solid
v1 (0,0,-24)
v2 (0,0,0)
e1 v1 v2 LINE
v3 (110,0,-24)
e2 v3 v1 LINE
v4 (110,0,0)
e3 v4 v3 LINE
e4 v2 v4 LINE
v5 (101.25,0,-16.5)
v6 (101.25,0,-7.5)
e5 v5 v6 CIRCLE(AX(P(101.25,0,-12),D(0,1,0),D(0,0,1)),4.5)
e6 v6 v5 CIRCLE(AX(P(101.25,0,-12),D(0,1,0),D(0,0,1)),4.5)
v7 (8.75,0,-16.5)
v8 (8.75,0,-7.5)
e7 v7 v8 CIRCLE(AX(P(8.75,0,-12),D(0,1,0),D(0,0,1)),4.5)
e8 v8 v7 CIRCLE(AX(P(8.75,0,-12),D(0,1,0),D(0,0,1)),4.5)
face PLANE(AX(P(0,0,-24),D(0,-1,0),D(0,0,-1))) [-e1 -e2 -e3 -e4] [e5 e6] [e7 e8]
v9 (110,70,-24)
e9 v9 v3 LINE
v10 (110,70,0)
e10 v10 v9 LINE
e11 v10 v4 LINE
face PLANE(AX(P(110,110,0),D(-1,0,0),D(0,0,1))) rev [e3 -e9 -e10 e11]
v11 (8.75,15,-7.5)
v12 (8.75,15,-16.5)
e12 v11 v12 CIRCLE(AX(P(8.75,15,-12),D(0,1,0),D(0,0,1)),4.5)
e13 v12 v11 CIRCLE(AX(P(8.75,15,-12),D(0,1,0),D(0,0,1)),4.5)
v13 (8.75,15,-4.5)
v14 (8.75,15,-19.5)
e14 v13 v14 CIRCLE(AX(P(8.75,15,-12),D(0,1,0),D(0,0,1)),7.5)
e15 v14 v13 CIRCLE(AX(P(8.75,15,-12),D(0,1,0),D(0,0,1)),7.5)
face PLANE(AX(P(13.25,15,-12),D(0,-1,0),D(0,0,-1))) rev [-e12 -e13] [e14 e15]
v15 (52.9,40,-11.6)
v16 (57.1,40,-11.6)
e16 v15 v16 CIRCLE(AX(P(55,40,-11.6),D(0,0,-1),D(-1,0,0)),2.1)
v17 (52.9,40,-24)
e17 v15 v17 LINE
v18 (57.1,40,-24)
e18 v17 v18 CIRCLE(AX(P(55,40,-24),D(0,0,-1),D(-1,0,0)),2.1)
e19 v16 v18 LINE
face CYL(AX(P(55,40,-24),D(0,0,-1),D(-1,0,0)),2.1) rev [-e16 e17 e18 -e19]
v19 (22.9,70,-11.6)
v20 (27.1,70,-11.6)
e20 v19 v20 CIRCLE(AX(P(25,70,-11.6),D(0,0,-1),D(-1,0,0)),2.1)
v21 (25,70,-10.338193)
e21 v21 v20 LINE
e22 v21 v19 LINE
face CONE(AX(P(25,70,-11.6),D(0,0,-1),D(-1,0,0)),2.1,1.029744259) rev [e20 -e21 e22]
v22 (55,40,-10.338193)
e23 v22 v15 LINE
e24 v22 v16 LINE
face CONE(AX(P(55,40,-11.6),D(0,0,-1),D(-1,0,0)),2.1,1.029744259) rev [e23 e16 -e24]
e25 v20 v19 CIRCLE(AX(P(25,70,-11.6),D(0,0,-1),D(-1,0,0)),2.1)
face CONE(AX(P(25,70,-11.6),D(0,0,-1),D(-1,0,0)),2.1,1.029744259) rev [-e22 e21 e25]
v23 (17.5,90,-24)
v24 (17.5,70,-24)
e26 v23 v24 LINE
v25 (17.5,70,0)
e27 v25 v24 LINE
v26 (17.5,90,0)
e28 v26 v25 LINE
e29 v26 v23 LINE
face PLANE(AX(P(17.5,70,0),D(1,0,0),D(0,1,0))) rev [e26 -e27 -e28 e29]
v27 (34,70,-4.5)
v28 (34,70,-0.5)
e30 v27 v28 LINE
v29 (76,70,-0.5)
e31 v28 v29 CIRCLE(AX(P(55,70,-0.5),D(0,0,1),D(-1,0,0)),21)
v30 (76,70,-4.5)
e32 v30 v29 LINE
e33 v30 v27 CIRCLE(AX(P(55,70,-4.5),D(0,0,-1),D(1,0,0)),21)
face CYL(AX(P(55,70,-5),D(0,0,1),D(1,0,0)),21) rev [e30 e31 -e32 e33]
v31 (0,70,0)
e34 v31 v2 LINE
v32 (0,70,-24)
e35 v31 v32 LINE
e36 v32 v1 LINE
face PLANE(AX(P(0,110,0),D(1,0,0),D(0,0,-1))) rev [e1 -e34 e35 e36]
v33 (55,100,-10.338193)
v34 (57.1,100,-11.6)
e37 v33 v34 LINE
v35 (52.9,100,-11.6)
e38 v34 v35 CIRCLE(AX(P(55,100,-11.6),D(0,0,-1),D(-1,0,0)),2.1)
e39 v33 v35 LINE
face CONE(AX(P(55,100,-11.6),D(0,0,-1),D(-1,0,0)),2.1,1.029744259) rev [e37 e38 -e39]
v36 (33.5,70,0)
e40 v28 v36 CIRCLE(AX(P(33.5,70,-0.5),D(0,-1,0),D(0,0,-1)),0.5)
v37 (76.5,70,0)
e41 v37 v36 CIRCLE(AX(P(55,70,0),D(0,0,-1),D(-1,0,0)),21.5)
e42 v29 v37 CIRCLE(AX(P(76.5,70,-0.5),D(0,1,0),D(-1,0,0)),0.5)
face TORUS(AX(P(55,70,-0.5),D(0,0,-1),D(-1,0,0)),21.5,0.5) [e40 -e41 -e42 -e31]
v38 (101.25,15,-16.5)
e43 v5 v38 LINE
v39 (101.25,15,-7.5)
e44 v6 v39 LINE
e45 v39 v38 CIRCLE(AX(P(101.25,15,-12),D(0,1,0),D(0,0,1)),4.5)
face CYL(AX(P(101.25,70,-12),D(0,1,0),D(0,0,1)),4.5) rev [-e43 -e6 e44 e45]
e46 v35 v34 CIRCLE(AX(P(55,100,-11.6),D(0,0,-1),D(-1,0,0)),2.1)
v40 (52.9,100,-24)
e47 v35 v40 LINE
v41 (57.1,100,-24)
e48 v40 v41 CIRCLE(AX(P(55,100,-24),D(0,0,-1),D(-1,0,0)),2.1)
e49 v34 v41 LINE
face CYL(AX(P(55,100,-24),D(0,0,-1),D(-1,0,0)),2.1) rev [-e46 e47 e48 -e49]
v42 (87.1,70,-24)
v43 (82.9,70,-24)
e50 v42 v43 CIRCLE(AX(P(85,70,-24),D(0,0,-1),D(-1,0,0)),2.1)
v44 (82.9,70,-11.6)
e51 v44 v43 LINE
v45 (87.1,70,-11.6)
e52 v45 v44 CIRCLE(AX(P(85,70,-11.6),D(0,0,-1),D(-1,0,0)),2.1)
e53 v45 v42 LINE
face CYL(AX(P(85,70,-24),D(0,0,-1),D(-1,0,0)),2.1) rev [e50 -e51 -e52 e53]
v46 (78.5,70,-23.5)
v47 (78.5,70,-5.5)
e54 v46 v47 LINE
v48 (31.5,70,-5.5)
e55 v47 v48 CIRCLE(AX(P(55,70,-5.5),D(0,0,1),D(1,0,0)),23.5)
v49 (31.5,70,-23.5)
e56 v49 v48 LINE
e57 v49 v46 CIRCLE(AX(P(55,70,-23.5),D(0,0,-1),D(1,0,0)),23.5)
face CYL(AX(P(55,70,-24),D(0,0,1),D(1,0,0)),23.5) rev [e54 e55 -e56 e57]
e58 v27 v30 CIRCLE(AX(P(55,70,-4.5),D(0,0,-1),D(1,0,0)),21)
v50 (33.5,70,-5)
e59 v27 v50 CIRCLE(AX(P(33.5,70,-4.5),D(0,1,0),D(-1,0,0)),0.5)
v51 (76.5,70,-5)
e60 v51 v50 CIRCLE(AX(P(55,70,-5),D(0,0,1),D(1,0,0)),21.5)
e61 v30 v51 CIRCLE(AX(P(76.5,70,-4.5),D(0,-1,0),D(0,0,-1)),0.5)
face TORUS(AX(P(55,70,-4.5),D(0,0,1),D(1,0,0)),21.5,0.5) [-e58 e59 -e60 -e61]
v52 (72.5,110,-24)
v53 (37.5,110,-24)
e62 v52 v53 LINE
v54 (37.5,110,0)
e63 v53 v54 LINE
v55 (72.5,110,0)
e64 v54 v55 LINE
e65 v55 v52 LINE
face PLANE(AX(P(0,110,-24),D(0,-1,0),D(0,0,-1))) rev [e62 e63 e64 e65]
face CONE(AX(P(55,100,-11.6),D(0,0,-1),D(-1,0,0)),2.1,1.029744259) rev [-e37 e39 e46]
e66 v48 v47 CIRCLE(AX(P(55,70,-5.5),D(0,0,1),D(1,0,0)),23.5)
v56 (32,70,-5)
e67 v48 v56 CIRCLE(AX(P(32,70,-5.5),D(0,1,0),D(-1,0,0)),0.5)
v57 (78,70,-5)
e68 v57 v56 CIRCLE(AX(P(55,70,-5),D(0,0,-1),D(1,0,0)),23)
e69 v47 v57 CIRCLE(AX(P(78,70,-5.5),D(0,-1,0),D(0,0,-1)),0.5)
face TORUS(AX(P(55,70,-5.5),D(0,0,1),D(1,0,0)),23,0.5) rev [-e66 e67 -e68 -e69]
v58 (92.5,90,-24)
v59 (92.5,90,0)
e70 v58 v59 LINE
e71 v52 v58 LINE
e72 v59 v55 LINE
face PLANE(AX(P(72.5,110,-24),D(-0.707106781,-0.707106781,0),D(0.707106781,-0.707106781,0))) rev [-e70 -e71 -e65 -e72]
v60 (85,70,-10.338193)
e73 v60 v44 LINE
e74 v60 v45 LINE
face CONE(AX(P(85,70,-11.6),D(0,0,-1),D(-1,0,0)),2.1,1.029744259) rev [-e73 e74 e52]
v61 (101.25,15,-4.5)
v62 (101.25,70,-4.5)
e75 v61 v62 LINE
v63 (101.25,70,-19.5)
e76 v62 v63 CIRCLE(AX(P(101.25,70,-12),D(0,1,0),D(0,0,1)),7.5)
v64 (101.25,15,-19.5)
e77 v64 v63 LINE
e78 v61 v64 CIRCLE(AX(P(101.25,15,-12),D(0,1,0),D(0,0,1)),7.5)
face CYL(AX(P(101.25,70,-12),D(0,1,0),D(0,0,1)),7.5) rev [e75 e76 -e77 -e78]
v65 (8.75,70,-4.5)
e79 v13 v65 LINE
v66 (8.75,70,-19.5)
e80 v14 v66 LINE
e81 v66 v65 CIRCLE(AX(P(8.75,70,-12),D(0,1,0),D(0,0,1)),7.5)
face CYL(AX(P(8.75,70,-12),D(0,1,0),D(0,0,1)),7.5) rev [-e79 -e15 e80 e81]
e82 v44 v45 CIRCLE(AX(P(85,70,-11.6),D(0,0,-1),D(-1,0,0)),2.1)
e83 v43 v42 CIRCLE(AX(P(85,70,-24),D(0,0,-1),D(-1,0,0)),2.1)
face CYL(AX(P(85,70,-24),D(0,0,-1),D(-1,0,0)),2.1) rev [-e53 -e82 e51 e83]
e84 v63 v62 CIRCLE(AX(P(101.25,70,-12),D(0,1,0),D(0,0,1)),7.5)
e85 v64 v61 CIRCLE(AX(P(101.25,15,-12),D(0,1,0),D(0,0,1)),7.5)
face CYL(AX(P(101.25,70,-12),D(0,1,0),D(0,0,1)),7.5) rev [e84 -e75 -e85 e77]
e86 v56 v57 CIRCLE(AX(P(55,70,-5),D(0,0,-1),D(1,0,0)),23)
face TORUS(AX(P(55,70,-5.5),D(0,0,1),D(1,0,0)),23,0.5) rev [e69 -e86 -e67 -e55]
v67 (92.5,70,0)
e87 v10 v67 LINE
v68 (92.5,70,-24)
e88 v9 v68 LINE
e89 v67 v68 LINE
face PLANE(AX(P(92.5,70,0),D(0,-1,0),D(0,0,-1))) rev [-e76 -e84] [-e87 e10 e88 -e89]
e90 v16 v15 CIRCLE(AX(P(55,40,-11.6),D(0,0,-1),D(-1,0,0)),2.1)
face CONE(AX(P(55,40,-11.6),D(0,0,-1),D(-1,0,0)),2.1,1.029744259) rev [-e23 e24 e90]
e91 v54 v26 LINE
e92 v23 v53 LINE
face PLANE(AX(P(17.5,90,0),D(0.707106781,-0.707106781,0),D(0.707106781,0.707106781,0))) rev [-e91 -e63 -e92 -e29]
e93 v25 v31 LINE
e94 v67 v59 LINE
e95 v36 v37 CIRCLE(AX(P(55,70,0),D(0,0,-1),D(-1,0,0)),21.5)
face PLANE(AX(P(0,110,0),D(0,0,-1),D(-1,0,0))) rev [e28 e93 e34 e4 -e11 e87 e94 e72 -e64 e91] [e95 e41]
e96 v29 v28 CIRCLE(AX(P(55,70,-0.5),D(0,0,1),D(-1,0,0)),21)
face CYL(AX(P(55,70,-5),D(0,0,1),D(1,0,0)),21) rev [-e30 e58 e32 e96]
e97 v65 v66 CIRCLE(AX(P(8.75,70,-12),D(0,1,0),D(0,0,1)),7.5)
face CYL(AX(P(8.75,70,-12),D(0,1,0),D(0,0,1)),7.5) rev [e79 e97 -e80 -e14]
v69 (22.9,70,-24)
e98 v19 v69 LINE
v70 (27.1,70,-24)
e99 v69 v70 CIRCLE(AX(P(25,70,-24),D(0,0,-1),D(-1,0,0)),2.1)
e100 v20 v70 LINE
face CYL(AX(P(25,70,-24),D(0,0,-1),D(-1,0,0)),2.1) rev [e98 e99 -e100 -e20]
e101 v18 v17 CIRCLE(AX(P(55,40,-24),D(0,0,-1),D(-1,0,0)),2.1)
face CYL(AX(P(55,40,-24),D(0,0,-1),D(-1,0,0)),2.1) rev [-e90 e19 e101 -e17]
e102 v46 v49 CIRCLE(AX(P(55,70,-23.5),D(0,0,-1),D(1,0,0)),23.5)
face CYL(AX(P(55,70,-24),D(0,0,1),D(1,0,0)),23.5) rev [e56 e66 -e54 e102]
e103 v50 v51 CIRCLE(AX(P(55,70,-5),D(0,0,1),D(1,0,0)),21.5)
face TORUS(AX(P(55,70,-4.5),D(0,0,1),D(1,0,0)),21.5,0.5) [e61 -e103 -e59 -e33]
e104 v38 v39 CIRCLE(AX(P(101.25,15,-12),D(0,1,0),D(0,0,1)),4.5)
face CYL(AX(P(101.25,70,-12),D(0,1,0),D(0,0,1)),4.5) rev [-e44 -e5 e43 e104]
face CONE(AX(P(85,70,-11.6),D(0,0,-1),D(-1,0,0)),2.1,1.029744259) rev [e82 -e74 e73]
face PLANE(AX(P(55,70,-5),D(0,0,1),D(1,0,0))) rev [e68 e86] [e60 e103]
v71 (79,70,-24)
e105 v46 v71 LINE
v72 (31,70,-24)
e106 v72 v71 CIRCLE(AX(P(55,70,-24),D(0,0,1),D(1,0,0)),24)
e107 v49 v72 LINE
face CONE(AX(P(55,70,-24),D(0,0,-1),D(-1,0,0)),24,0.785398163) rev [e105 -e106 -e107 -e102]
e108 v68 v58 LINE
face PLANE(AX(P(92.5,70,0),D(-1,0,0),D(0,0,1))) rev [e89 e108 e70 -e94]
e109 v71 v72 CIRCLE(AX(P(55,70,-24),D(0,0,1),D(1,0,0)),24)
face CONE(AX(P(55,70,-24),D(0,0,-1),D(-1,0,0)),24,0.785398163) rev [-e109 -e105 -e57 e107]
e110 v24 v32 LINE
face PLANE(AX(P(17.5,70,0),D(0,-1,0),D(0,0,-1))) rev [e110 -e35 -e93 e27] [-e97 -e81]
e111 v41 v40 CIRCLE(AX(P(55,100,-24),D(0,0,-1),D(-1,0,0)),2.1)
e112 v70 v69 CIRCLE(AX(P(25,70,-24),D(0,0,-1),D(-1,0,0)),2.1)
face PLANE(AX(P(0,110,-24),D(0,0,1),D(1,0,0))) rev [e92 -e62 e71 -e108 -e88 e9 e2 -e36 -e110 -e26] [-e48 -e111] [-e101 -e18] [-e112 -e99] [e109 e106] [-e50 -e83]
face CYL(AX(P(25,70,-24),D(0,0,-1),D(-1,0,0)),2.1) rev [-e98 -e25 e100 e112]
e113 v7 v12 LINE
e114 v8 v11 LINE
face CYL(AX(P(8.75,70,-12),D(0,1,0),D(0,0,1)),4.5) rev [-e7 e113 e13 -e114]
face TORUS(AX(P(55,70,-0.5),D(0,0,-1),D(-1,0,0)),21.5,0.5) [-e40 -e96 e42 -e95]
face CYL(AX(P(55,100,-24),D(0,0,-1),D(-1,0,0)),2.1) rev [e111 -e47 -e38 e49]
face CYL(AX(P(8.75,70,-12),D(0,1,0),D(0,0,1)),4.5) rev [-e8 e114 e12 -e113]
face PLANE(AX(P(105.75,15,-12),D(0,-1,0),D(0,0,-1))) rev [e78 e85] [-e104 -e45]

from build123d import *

# Parameters (mm, degrees)
SKETCH_1_W                = 110
SKETCH_1_H                = 24
EXTRUDE_1_DEPTH           = 110
SKETCH_2_R                = 21
CUT_EXTRUDE_1_DEPTH       = 5
SKETCH_3_R                = 23.5
CUT_EXTRUDE_2_DEPTH       = 19
SKETCH_5_W                = 17.5
SKETCH_5_H                = 40
CUT_EXTRUDE_3_DEPTH       = 158.40393896
CHAMFER_1_SIZE            = 20
HOLE_WIZARD_M5_1_D        = 4.2
HOLE_WIZARD_M5_1_DEPTH    = 12.4
HOLE_WIZARD_M5_1_TIP      = 1.2618073
HOLE_WIZARD_1_D           = 9
HOLE_WIZARD_1_CBORE_D     = 15
HOLE_WIZARD_1_CBORE_DEPTH = 55
FILLET_2_R                = 0.5
CHAMFER_2_SIZE            = 0.5


with BuildPart() as part:
    # 草图1 → 拉伸1 (new body)
    with BuildSketch(Plane(origin=(0, 0, 0), x_dir=(1, 0, 0), z_dir=(0, 1, 0))):
        with Locations((55, 12)):
            Rectangle(SKETCH_1_W, SKETCH_1_H)
    extrude(amount=EXTRUDE_1_DEPTH)

    # 草图2 → 切除-拉伸1 (cut)
    with BuildSketch(Plane.XY):
        with Locations((55, 70)):
            Circle(SKETCH_2_R)
    extrude(amount=-CUT_EXTRUDE_1_DEPTH, mode=Mode.SUBTRACT)

    # 草图3 → 切除-拉伸2 (cut)
    with BuildSketch(Plane.XY.offset(-5)):
        with Locations((55, 70)):
            Circle(SKETCH_3_R)
    extrude(amount=-CUT_EXTRUDE_2_DEPTH, mode=Mode.SUBTRACT)

    # 草图5 → 切除-拉伸3 (cut, through all)
    with BuildSketch(Plane(origin=(0, 0, -24), x_dir=(-1, 0, 0), z_dir=(0, 0, -1))):
        with Locations((-101.25, 90)):
            Rectangle(SKETCH_5_W, SKETCH_5_H)
        with Locations((-8.75, 90)):
            Rectangle(SKETCH_5_W, SKETCH_5_H)
    extrude(amount=-CUT_EXTRUDE_3_DEPTH, mode=Mode.SUBTRACT)

    # 倒角1
    chamfer_1_edges = [part.edges().sort_by_distance(p)[0] for p in [
        (92.5, 110, -12),
        (17.5, 110, -12),
    ]]
    chamfer(chamfer_1_edges, length=CHAMFER_1_SIZE)

    # M5 螺纹孔1
    with Locations(Plane(origin=(55, 100, -24), x_dir=(-1, 0, 0), z_dir=(0, 0, -1))):
        with Locations((0, 0), (-30, -30), (0, -60), (30, -30)):
            Hole(HOLE_WIZARD_M5_1_D / 2, depth=HOLE_WIZARD_M5_1_DEPTH)
            with Locations((0, 0, -(HOLE_WIZARD_M5_1_DEPTH + HOLE_WIZARD_M5_1_TIP / 2))):  # 118° drill point
                Cone(0, HOLE_WIZARD_M5_1_D / 2, HOLE_WIZARD_M5_1_TIP, mode=Mode.SUBTRACT)

    # 打孔尺寸根据内六角圆柱头螺钉的类型1 (through all)
    with Locations(Plane(origin=(8.75, 70, -12), x_dir=(0, 0, 1), z_dir=(0, 1, 0))):
        with Locations((0, 0), (0, 92.5)):
            CounterBoreHole(HOLE_WIZARD_1_D / 2, HOLE_WIZARD_1_CBORE_D / 2, HOLE_WIZARD_1_CBORE_DEPTH)

    # 圆角2
    fillet_2_edges = [part.edges().sort_by_distance(p)[0] for p in [
        (34, 70, 0),
        (31.5, 70, -5),
        (34, 70, -5),
    ]]
    fillet(fillet_2_edges, radius=FILLET_2_R)

    # 倒角2
    chamfer_2_edges = [part.edges().sort_by_distance(p)[0] for p in [
        (31.5, 70, -24),
    ]]
    chamfer(chamfer_2_edges, length=CHAMFER_2_SIZE)


solid = part.part
